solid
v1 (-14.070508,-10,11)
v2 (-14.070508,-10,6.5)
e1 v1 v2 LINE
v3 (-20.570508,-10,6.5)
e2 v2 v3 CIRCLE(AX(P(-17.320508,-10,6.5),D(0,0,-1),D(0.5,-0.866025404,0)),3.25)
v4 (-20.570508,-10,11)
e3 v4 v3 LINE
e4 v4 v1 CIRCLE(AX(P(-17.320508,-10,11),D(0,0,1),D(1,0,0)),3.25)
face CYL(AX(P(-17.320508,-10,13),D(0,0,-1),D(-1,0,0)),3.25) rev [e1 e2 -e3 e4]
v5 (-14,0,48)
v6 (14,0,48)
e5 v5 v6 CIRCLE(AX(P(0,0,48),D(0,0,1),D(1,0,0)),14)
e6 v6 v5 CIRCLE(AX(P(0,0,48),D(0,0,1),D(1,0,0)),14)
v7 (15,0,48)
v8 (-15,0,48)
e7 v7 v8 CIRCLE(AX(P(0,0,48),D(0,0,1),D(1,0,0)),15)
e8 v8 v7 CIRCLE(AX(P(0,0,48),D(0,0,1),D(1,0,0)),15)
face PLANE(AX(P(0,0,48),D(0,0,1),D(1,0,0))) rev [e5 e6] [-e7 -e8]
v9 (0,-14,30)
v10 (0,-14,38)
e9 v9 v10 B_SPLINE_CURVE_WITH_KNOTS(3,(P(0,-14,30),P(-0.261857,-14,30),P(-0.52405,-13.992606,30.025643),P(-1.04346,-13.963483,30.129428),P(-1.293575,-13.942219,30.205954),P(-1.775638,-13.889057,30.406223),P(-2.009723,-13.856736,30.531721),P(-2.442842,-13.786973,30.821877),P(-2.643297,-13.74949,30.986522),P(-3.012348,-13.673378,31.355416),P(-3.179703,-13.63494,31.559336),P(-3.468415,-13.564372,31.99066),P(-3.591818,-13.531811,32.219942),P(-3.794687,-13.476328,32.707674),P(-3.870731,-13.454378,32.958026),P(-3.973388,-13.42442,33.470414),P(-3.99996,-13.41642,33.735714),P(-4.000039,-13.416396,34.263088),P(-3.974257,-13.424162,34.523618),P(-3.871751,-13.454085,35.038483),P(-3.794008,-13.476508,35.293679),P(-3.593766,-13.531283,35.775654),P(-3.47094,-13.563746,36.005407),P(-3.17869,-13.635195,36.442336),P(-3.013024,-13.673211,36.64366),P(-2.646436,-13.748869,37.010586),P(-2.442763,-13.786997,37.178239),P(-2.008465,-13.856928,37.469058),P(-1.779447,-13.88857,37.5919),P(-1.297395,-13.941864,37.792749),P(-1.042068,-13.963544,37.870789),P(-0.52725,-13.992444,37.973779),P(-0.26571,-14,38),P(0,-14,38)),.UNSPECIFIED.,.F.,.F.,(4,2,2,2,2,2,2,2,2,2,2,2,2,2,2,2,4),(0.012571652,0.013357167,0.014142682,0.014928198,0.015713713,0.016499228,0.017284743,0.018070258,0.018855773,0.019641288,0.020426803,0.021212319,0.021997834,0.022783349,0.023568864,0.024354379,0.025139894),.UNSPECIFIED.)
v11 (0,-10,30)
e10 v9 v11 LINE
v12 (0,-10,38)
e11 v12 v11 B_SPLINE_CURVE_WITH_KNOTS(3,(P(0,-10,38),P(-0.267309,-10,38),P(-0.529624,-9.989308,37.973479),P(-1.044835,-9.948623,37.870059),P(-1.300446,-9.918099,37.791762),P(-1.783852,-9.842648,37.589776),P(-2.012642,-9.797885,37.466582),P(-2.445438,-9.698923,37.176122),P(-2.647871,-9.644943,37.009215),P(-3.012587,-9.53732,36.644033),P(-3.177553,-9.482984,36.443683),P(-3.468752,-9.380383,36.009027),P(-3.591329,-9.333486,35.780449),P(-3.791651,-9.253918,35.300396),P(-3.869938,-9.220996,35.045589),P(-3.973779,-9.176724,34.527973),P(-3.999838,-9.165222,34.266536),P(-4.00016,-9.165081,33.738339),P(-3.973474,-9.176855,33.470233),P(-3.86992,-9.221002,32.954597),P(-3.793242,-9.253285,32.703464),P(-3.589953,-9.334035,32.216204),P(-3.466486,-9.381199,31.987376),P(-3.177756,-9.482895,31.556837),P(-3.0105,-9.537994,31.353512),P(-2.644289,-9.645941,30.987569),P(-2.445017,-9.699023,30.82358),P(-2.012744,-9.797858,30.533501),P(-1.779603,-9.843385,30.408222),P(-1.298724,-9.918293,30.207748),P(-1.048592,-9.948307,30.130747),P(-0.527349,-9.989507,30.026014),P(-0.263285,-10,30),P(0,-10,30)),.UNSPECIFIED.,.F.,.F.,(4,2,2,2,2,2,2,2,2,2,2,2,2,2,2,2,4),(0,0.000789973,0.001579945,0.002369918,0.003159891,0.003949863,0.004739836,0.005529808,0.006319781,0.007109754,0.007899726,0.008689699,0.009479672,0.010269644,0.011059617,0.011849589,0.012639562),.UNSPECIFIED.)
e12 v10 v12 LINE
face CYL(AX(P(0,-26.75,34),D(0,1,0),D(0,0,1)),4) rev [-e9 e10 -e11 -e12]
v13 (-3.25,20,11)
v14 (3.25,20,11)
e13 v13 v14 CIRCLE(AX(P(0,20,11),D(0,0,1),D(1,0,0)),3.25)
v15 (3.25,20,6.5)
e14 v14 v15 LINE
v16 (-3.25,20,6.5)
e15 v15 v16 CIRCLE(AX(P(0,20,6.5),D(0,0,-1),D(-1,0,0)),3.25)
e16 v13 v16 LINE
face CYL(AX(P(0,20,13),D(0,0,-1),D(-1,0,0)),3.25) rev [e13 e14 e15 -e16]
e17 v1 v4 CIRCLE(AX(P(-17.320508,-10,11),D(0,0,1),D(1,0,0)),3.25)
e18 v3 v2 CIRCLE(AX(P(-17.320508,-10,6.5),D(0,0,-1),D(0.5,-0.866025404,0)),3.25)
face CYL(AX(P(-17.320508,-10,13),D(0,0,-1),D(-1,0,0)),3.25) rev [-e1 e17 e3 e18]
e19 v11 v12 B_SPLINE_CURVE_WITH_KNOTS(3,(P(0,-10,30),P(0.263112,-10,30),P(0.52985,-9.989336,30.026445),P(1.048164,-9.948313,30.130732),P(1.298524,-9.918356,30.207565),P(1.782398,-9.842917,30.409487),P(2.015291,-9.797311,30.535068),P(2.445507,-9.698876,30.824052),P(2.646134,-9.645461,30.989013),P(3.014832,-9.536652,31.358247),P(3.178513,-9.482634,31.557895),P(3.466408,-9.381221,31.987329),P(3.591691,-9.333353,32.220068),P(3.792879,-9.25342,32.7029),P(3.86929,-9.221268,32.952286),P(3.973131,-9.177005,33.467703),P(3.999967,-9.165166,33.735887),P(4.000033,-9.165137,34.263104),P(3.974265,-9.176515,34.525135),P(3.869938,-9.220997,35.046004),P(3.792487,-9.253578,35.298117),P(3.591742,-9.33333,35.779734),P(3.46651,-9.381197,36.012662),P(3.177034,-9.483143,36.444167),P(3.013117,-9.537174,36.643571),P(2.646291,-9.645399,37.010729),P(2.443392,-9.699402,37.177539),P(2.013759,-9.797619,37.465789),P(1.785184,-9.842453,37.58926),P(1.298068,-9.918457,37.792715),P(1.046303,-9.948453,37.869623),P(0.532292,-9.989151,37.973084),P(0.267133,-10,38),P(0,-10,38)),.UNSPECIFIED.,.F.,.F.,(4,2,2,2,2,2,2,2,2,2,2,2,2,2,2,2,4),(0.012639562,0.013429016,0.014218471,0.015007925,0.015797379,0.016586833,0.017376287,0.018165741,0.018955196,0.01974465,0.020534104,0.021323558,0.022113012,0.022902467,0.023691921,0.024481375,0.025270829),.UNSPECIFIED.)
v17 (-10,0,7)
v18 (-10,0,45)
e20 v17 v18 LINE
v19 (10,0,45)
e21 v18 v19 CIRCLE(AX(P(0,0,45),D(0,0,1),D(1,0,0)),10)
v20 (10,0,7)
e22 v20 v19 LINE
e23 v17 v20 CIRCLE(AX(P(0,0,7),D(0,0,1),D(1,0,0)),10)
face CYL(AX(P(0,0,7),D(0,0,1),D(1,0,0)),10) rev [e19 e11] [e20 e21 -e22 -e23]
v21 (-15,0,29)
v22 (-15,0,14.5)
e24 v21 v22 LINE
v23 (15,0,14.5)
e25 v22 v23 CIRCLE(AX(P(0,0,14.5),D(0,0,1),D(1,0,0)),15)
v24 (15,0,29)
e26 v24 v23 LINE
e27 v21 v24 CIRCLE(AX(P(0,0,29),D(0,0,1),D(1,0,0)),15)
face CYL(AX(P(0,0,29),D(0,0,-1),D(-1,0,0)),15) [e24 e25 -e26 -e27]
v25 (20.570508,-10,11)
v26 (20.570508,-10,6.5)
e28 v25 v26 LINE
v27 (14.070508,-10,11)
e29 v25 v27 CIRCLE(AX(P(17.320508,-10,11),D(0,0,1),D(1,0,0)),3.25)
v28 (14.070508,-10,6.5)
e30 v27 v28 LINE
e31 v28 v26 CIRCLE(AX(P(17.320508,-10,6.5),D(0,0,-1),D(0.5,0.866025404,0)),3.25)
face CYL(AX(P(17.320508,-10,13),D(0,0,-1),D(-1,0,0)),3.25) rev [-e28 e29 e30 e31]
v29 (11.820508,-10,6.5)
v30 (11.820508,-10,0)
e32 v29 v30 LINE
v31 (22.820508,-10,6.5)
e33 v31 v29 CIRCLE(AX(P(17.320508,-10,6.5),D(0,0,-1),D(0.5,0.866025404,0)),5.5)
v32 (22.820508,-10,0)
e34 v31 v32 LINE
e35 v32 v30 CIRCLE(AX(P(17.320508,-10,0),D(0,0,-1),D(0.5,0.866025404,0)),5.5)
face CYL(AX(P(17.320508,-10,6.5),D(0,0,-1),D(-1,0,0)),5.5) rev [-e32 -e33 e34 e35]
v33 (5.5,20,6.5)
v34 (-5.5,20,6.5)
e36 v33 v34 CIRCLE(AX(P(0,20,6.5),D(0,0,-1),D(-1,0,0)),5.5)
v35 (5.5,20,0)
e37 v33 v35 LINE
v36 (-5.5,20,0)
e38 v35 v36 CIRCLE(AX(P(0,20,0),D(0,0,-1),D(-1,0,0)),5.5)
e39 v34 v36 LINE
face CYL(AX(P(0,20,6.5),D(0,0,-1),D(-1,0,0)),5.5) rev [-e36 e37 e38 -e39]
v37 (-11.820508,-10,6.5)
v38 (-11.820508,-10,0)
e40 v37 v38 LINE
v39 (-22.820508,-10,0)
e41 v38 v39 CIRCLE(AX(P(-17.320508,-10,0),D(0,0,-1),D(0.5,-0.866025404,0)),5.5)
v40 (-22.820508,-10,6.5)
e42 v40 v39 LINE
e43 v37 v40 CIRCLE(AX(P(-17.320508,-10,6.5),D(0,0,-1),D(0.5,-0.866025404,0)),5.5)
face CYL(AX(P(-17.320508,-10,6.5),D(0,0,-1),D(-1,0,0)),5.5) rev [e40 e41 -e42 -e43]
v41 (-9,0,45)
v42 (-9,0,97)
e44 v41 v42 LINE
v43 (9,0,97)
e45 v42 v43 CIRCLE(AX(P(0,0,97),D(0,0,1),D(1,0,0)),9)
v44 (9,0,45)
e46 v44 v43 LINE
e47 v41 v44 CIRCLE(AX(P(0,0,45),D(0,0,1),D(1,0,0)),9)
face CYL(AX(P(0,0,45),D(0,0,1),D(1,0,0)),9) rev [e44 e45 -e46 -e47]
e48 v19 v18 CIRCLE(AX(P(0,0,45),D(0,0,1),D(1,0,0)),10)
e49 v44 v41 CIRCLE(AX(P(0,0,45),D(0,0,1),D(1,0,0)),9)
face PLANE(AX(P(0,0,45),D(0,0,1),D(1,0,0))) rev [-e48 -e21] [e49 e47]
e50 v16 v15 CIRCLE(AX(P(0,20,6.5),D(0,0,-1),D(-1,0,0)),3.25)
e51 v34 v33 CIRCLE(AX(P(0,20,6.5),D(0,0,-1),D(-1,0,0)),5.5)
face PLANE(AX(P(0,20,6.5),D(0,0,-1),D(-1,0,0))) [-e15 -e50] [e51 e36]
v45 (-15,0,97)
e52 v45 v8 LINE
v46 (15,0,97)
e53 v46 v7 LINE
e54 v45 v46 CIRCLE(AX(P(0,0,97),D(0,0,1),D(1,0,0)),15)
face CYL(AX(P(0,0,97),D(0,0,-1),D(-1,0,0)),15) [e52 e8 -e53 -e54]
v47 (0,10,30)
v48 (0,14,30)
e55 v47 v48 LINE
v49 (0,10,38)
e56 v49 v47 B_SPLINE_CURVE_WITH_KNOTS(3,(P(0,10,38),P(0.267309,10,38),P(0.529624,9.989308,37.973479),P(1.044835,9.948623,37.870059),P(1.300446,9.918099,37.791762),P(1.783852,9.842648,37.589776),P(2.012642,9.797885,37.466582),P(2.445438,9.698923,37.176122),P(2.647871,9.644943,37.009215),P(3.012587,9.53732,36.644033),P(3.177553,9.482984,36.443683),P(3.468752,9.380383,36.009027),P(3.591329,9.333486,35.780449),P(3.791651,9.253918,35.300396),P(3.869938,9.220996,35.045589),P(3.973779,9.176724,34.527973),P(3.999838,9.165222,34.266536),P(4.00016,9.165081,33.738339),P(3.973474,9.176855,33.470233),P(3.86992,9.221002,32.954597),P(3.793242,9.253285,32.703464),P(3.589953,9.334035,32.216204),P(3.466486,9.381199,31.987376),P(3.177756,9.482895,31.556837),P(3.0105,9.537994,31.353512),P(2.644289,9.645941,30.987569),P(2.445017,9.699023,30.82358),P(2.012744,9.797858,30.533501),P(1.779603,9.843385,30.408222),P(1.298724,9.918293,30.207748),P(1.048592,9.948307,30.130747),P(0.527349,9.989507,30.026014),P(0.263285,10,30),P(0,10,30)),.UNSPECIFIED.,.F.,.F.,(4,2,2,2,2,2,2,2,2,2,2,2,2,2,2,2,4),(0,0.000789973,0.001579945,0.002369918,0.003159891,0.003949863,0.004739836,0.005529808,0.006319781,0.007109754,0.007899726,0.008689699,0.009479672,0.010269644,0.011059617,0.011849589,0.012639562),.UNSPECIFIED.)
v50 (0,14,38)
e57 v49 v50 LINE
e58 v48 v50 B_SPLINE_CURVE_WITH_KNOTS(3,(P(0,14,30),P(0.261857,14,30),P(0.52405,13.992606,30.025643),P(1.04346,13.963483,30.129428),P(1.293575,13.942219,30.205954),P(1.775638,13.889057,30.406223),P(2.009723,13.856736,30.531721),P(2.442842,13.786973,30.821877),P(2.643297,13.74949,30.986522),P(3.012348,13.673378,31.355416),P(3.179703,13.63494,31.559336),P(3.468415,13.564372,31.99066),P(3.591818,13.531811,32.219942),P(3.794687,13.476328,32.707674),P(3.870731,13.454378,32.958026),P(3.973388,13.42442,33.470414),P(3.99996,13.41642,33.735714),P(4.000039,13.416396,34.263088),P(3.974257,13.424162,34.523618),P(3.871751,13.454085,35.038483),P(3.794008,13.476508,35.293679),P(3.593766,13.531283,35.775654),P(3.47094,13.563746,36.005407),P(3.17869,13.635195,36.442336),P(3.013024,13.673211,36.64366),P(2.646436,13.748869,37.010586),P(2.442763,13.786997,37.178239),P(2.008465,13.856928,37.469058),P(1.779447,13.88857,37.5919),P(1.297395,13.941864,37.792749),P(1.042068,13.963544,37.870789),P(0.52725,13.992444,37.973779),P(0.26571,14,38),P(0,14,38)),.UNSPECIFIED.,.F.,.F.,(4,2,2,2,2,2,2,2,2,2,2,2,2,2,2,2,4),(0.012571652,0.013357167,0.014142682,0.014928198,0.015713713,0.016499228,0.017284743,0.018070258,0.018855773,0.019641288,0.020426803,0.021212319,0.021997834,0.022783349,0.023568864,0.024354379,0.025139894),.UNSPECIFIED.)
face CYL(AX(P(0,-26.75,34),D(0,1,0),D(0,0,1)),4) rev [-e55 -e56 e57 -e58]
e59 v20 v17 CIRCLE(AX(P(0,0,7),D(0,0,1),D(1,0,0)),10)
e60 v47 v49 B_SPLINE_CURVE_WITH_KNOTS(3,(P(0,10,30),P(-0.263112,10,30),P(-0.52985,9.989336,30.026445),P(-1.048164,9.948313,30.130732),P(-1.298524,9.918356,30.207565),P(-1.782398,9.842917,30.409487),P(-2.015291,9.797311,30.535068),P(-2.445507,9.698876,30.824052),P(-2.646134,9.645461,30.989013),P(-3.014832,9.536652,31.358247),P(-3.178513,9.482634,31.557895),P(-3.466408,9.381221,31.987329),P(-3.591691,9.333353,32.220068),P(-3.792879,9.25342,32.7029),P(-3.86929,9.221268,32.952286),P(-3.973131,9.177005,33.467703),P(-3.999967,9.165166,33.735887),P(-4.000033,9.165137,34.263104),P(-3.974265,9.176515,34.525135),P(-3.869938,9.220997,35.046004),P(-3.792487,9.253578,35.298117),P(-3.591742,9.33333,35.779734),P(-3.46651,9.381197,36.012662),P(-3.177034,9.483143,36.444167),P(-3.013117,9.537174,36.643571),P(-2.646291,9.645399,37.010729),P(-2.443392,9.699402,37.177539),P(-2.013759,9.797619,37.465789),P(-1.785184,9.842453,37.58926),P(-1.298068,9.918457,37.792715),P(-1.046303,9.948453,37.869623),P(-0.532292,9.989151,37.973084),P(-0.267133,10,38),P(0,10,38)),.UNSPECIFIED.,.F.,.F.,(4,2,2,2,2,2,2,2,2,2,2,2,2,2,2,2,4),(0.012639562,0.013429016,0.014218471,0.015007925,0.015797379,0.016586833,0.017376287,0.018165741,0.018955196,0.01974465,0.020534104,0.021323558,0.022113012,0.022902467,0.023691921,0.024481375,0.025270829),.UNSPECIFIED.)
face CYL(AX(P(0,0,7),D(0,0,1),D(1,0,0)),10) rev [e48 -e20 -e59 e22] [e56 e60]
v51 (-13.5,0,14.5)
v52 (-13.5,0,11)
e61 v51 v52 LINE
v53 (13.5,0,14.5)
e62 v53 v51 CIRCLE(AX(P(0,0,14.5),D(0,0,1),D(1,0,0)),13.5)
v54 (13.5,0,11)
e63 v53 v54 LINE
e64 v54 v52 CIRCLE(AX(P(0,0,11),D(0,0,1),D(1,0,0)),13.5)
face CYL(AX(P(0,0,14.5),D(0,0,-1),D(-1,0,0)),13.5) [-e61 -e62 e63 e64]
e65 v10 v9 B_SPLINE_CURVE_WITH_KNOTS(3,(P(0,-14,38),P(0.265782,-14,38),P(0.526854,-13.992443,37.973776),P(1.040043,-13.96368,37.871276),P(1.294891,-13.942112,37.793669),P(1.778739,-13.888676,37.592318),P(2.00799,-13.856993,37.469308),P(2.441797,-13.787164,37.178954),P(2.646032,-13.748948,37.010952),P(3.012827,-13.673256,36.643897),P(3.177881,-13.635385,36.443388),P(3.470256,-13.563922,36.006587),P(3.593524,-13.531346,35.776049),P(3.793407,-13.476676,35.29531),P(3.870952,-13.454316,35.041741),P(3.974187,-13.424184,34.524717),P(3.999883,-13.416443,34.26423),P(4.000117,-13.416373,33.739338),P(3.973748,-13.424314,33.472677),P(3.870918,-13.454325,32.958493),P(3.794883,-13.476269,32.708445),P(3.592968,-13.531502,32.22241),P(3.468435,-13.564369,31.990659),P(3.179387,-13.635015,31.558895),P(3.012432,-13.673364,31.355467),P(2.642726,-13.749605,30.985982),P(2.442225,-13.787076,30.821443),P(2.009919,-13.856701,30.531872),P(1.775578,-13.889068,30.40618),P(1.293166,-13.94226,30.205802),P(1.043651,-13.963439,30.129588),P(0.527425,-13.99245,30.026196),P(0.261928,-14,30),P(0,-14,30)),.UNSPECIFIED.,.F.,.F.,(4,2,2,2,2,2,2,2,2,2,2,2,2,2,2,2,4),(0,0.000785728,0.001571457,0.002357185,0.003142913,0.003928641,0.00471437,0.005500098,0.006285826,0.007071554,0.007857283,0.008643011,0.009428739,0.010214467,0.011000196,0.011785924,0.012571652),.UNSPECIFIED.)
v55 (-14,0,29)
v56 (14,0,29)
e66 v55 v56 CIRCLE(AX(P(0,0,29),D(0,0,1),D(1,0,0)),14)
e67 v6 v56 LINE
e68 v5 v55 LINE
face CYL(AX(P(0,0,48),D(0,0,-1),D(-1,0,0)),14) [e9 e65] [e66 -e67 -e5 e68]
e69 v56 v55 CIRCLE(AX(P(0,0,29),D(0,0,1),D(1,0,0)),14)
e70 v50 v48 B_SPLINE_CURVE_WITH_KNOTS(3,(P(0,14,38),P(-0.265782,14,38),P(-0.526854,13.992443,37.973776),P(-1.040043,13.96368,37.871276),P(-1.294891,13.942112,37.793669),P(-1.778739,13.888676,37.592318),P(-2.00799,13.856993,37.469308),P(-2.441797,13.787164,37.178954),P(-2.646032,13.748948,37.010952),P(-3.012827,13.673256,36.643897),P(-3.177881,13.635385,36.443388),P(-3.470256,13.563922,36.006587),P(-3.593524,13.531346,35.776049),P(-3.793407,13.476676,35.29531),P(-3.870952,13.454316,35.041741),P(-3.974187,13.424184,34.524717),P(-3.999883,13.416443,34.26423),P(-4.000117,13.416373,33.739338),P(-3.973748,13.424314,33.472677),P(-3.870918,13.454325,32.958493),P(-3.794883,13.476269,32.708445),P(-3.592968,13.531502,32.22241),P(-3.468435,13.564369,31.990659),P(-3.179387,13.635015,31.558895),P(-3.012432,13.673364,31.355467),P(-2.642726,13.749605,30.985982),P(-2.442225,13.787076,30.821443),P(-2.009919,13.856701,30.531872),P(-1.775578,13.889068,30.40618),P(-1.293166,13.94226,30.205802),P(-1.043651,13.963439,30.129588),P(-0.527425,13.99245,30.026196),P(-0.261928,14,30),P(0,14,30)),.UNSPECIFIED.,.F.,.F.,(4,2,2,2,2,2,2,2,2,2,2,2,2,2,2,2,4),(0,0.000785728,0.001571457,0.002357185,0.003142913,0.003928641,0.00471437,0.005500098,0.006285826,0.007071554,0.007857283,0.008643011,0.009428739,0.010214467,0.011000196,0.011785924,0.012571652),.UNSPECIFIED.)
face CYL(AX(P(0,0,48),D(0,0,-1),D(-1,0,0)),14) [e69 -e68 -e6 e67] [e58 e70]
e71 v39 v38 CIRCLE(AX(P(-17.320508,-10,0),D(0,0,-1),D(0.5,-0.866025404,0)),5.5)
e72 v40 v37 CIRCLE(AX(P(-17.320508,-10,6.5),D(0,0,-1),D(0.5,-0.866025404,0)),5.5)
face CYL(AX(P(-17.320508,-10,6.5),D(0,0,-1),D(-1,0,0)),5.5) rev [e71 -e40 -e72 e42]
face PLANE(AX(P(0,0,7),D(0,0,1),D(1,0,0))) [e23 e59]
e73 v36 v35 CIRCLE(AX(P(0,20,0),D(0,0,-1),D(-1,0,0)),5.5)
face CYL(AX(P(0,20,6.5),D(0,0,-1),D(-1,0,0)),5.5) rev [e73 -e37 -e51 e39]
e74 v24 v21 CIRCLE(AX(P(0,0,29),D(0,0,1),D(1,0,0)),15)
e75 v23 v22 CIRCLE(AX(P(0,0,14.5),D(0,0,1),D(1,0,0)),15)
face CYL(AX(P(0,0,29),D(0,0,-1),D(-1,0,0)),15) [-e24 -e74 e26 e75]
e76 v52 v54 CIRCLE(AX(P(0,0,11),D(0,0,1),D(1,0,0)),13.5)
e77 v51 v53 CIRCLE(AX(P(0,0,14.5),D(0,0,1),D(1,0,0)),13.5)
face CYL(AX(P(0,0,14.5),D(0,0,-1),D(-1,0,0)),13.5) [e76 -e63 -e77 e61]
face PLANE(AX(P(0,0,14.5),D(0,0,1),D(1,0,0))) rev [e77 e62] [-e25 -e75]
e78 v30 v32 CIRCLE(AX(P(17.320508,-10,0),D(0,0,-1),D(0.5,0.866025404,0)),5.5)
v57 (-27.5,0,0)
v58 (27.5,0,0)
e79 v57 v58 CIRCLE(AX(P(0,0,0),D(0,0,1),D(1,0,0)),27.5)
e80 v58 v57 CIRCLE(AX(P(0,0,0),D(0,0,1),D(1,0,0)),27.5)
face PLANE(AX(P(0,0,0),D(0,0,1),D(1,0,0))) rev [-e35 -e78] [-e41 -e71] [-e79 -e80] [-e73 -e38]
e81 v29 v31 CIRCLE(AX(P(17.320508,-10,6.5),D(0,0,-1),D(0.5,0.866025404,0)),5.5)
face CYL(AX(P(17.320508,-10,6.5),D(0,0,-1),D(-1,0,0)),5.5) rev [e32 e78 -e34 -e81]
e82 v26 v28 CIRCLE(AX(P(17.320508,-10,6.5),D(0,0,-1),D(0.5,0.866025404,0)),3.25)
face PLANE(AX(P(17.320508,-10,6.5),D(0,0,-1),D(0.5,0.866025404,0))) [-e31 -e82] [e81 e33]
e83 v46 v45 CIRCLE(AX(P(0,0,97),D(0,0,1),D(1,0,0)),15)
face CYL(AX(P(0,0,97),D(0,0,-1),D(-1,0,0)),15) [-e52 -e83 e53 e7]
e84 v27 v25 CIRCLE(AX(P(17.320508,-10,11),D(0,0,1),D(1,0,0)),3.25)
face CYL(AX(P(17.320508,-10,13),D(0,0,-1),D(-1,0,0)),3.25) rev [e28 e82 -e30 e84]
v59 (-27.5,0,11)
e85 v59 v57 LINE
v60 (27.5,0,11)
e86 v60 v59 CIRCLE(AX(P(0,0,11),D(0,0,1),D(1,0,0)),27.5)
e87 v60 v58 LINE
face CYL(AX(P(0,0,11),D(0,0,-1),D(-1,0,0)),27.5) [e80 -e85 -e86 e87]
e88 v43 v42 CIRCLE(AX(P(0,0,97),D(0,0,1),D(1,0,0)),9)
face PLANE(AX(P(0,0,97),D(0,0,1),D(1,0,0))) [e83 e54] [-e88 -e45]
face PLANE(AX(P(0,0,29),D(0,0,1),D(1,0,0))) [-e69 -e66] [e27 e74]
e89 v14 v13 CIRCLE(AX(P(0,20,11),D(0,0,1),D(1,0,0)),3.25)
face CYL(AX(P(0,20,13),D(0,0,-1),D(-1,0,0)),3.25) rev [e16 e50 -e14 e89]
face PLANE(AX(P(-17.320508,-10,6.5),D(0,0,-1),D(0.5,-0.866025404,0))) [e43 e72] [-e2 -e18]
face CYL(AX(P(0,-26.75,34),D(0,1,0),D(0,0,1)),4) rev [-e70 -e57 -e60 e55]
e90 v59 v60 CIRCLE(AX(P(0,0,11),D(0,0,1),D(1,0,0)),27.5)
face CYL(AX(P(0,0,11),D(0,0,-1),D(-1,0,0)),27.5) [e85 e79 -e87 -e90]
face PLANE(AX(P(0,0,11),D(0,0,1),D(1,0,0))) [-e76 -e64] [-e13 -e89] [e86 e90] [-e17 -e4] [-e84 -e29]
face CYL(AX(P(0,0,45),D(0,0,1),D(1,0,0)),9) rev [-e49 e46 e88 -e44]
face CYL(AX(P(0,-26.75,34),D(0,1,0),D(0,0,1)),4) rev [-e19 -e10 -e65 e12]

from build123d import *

# Parameters (mm, degrees)
SKETCH1_R           = 27.5
BOSS_EXTRUDE1_DEPTH = 11
SKETCH2_R           = 13.5
BOSS_EXTRUDE2_DEPTH = 3.5
SKETCH3_R           = 15
BOSS_EXTRUDE3_DEPTH = 14.5
SKETCH4_R           = 14
BOSS_EXTRUDE4_DEPTH = 19
SKETCH5_R           = 15
BOSS_EXTRUDE5_DEPTH = 49
SKETCH6_R           = 9
CUT_EXTRUDE1_DEPTH  = 52
SKETCH7_R           = 10
CUT_EXTRUDE2_DEPTH  = 38
SKETCH8_R           = 5.5
CUT_EXTRUDE3_DEPTH  = 6.5
SKETCH9_R           = 3.25
CUT_EXTRUDE4_DEPTH  = 6.5
CIRPATTERN1_COUNT   = 3
SKETCH10_R          = 4
CUT_EXTRUDE5_DEPTH  = 26.75


with BuildPart() as part:
    # Sketch1 → Boss-Extrude1 (new body)
    with BuildSketch(Plane.XY):
        Circle(SKETCH1_R)
    extrude(amount=BOSS_EXTRUDE1_DEPTH)

    # Sketch2 → Boss-Extrude2 (add)
    with BuildSketch(Plane.XY.offset(11)):
        Circle(SKETCH2_R)
    extrude(amount=BOSS_EXTRUDE2_DEPTH)

    # Sketch3 → Boss-Extrude3 (add)
    with BuildSketch(Plane.XY.offset(14.5)):
        with Locations(Location((0, 0, 0), (0, 0, 180))):
            Circle(SKETCH3_R)
    extrude(amount=BOSS_EXTRUDE3_DEPTH)

    # Sketch4 → Boss-Extrude4 (add)
    with BuildSketch(Plane.XY.offset(29)):
        Circle(SKETCH4_R)
    extrude(amount=BOSS_EXTRUDE4_DEPTH)

    # Sketch5 → Boss-Extrude5 (add)
    with BuildSketch(Plane.XY.offset(48)):
        with Locations(Location((0, 0, 0), (0, 0, 180))):
            Circle(SKETCH5_R)
    extrude(amount=BOSS_EXTRUDE5_DEPTH)

    # Sketch6 → Cut-Extrude1 (cut)
    with BuildSketch(Plane.XY.offset(97)):
        Circle(SKETCH6_R)
    extrude(amount=-CUT_EXTRUDE1_DEPTH, mode=Mode.SUBTRACT)

    # Sketch7 → Cut-Extrude2 (cut)
    with BuildSketch(Plane.XY.offset(45)):
        Circle(SKETCH7_R)
    extrude(amount=-CUT_EXTRUDE2_DEPTH, mode=Mode.SUBTRACT)

    # Sketch8 → Cut-Extrude3 (cut)
    with BuildSketch(Plane(origin=(0, 0, 0), x_dir=(-1, 0, 0), z_dir=(0, 0, -1))):
        with Locations((0, 20)):
            Circle(SKETCH8_R)
    cut_extrude3 = extrude(amount=-CUT_EXTRUDE3_DEPTH, mode=Mode.SUBTRACT)

    # Sketch9 → Cut-Extrude4 (cut)
    with BuildSketch(Plane(origin=(0, 0, 6.5), x_dir=(-1, 0, 0), z_dir=(0, 0, -1))):
        with Locations((0, 20)):
            Circle(SKETCH9_R)
    cut_extrude4 = extrude(amount=-CUT_EXTRUDE4_DEPTH, mode=Mode.SUBTRACT)

    # CirPattern1: Cut-Extrude3, Cut-Extrude4 ×3 about axis
    cirpattern1_axis = Axis((0, 0, 0), (0, 0, 1))
    add([cut_extrude3.rotate(cirpattern1_axis, i * 360 / CIRPATTERN1_COUNT) for i in range(1, CIRPATTERN1_COUNT)], mode=Mode.SUBTRACT)
    add([cut_extrude4.rotate(cirpattern1_axis, i * 360 / CIRPATTERN1_COUNT) for i in range(1, CIRPATTERN1_COUNT)], mode=Mode.SUBTRACT)

    # Sketch10 → Cut-Extrude5 (cut, symmetric)
    with BuildSketch(Plane(origin=(0, 0, 0), x_dir=(1, 0, 0), z_dir=(0, 1, 0))):
        with Locations(Location((0, -34, 0), (0, 0, 270))):
            Circle(SKETCH10_R)
    extrude(amount=CUT_EXTRUDE5_DEPTH, both=True, mode=Mode.SUBTRACT)


solid = part.part
